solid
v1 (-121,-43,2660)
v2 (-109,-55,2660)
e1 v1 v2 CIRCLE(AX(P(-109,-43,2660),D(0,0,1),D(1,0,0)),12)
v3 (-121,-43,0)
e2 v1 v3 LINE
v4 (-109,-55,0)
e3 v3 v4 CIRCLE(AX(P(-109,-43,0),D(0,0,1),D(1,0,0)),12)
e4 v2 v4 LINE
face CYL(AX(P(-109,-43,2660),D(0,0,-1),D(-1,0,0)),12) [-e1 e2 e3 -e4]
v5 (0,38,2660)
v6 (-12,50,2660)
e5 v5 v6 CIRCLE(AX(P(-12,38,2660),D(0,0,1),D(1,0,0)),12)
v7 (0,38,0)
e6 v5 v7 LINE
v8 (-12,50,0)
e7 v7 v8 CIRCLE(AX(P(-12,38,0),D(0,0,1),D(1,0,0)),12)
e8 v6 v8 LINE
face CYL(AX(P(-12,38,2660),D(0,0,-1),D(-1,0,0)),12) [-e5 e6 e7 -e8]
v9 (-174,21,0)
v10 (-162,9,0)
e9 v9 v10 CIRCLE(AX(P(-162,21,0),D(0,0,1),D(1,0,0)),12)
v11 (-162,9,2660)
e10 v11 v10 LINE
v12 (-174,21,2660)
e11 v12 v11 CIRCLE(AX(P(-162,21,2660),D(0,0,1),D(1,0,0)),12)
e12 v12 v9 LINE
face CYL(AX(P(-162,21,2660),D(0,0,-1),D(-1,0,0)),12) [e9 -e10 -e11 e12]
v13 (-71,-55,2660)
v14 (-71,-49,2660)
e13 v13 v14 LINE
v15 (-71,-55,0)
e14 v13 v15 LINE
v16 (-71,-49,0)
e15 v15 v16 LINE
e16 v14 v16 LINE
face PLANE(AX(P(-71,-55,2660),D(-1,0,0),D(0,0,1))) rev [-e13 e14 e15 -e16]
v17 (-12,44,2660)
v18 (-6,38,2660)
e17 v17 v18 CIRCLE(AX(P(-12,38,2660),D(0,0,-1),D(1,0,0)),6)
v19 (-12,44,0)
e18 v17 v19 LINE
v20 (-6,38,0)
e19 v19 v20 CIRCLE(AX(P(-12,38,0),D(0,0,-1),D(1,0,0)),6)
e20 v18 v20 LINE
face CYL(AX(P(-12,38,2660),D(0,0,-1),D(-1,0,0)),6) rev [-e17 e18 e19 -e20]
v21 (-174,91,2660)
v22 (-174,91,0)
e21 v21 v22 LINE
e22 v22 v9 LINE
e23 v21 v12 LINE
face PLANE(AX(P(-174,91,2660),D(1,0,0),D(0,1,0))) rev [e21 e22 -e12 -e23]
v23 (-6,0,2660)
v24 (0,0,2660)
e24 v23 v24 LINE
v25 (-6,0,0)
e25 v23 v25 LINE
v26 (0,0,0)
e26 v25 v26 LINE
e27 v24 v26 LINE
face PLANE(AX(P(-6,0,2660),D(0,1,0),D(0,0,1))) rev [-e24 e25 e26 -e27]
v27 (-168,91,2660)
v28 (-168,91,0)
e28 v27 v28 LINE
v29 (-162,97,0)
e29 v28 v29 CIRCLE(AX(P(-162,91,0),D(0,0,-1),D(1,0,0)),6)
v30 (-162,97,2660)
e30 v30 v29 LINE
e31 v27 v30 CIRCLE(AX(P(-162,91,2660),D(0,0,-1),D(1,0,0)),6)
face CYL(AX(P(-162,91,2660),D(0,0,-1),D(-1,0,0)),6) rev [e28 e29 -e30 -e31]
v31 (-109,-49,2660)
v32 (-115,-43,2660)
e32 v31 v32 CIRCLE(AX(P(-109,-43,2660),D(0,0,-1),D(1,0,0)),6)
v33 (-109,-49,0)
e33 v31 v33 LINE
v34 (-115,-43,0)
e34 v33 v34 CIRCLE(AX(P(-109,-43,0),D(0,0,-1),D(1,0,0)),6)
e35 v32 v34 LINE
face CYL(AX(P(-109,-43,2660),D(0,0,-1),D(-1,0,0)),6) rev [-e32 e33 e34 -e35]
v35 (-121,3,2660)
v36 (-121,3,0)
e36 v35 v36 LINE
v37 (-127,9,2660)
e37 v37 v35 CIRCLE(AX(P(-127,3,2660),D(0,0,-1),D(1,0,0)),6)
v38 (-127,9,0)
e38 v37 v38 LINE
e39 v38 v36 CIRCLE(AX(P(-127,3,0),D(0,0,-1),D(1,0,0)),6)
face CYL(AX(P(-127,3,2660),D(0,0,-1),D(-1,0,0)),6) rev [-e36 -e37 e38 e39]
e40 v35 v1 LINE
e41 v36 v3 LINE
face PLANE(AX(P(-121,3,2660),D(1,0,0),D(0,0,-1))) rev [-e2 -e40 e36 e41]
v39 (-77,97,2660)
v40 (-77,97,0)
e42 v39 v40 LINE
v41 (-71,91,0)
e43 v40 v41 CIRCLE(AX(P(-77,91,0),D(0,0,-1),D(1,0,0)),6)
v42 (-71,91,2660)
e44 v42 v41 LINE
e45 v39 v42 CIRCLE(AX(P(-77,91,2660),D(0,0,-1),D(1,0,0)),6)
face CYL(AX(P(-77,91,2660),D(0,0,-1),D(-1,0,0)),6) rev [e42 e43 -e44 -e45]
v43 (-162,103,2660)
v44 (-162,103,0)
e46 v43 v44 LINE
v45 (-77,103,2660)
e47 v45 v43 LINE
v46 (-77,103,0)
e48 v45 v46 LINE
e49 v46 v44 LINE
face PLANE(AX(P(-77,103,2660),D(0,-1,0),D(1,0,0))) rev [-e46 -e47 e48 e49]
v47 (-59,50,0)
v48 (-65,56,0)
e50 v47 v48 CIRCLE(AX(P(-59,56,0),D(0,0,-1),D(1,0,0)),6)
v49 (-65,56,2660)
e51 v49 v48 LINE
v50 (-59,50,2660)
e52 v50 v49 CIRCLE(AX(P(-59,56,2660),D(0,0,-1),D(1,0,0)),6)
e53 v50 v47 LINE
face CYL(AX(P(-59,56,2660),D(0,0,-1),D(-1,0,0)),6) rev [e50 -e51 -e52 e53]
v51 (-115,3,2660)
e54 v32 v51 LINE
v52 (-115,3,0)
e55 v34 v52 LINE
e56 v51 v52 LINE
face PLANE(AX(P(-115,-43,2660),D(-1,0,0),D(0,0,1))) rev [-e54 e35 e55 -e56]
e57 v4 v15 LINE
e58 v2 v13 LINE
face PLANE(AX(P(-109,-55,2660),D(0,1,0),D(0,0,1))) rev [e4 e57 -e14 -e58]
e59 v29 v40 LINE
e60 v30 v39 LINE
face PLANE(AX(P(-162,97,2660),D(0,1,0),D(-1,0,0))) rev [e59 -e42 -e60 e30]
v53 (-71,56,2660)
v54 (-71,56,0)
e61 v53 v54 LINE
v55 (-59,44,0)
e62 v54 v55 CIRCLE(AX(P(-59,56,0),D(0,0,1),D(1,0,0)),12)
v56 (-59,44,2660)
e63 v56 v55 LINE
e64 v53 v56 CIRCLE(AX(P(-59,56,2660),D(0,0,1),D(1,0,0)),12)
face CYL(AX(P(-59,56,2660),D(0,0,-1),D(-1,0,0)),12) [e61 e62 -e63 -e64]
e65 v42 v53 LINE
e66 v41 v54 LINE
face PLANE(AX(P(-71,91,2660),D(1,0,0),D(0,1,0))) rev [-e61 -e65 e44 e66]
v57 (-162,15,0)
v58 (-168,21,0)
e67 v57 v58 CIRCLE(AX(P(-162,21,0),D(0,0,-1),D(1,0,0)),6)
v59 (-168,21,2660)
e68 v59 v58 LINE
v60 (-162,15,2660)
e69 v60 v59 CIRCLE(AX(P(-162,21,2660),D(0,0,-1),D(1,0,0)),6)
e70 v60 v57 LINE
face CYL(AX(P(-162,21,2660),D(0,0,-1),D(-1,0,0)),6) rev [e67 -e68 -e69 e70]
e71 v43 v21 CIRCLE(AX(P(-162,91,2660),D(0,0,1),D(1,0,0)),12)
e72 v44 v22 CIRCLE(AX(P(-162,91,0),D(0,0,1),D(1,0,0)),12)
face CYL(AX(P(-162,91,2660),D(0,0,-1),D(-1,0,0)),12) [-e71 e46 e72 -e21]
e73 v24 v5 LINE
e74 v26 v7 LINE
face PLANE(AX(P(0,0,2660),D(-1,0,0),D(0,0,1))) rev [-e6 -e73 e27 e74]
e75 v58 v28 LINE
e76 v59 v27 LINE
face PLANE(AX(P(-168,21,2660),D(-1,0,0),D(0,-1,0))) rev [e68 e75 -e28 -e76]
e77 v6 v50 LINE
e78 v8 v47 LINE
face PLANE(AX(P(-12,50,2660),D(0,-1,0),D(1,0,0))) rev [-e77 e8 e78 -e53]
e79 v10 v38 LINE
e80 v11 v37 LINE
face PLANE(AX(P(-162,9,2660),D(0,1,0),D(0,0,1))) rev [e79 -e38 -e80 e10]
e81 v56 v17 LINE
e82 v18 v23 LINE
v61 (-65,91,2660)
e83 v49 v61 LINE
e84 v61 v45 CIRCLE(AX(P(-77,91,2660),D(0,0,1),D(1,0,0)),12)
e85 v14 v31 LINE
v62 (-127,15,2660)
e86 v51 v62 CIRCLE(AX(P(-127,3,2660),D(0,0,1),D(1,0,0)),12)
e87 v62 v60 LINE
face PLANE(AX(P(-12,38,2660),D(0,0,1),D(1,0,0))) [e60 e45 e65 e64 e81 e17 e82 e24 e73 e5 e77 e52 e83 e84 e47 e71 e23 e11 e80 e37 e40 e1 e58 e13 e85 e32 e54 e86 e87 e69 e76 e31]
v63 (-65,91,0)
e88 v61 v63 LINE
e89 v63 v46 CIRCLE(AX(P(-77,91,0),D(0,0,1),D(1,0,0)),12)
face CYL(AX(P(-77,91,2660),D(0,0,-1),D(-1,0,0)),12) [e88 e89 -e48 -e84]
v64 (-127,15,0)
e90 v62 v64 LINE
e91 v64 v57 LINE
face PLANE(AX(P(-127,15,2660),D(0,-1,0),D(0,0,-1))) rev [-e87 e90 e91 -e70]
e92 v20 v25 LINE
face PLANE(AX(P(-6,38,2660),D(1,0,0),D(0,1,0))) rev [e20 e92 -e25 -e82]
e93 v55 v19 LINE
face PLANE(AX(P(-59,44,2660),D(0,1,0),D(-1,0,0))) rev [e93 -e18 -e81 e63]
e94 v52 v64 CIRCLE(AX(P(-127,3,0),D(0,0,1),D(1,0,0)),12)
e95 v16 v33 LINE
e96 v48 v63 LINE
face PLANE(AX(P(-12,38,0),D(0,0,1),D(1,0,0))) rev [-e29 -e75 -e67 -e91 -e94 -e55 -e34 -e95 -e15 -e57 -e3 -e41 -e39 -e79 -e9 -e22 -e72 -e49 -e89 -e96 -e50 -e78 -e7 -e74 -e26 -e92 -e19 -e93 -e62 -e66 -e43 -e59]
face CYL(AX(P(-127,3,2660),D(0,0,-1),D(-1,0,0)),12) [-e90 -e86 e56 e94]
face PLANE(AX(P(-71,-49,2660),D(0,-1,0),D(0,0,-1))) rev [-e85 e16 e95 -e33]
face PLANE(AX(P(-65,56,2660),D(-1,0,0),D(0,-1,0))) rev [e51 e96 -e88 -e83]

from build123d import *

# Parameters (mm, degrees)
BOSS_EXTRUDE1_DEPTH = 2660


with BuildPart() as part:
    # Sketch1 → Boss-Extrude1 (new body)
    with BuildSketch(Plane.XY):
        with BuildLine():
            Line((0, 0), (0, 38))
            ThreePointArc((0, 38), (-3.514718626, 46.485281374), (-12, 50))
            Line((-12, 50), (-59, 50))
            ThreePointArc((-59, 50), (-63.242640687, 51.757359313), (-65, 56))
            Line((-65, 56), (-65, 91))
            ThreePointArc((-65, 91), (-68.514718626, 99.485281374), (-77, 103))
            Line((-77, 103), (-162, 103))
            ThreePointArc((-162, 103), (-170.485281374, 99.485281374), (-174, 91))
            Line((-174, 91), (-174, 21))
            ThreePointArc((-174, 21), (-170.485281374, 12.514718626), (-162, 9))
            Line((-162, 9), (-127, 9))
            ThreePointArc((-127, 9), (-122.757359313, 7.242640687), (-121, 3))
            Line((-121, 3), (-121, -43))
            ThreePointArc((-121, -43), (-117.485281374, -51.485281374), (-109, -55))
            Line((-109, -55), (-71, -55))
            Line((-71, -55), (-71, -49))
            Line((-71, -49), (-109, -49))
            ThreePointArc((-109, -49), (-113.242640687, -47.242640687), (-115, -43))
            Line((-115, -43), (-115, 3))
            ThreePointArc((-115, 3), (-118.514718626, 11.485281374), (-127, 15))
            Line((-127, 15), (-162, 15))
            ThreePointArc((-162, 15), (-166.242640687, 16.757359313), (-168, 21))
            Line((-168, 21), (-168, 91))
            ThreePointArc((-168, 91), (-166.242640687, 95.242640687), (-162, 97))
            Line((-162, 97), (-77, 97))
            ThreePointArc((-77, 97), (-72.757359313, 95.242640687), (-71, 91))
            Line((-71, 91), (-71, 56))
            ThreePointArc((-71, 56), (-67.485281374, 47.514718626), (-59, 44))
            Line((-59, 44), (-12, 44))
            ThreePointArc((-12, 44), (-7.757359313, 42.242640687), (-6, 38))
            Line((-6, 38), (-6, 0))
            Line((-6, 0), (0, 0))
        make_face()
    extrude(amount=BOSS_EXTRUDE1_DEPTH)


solid = part.part
